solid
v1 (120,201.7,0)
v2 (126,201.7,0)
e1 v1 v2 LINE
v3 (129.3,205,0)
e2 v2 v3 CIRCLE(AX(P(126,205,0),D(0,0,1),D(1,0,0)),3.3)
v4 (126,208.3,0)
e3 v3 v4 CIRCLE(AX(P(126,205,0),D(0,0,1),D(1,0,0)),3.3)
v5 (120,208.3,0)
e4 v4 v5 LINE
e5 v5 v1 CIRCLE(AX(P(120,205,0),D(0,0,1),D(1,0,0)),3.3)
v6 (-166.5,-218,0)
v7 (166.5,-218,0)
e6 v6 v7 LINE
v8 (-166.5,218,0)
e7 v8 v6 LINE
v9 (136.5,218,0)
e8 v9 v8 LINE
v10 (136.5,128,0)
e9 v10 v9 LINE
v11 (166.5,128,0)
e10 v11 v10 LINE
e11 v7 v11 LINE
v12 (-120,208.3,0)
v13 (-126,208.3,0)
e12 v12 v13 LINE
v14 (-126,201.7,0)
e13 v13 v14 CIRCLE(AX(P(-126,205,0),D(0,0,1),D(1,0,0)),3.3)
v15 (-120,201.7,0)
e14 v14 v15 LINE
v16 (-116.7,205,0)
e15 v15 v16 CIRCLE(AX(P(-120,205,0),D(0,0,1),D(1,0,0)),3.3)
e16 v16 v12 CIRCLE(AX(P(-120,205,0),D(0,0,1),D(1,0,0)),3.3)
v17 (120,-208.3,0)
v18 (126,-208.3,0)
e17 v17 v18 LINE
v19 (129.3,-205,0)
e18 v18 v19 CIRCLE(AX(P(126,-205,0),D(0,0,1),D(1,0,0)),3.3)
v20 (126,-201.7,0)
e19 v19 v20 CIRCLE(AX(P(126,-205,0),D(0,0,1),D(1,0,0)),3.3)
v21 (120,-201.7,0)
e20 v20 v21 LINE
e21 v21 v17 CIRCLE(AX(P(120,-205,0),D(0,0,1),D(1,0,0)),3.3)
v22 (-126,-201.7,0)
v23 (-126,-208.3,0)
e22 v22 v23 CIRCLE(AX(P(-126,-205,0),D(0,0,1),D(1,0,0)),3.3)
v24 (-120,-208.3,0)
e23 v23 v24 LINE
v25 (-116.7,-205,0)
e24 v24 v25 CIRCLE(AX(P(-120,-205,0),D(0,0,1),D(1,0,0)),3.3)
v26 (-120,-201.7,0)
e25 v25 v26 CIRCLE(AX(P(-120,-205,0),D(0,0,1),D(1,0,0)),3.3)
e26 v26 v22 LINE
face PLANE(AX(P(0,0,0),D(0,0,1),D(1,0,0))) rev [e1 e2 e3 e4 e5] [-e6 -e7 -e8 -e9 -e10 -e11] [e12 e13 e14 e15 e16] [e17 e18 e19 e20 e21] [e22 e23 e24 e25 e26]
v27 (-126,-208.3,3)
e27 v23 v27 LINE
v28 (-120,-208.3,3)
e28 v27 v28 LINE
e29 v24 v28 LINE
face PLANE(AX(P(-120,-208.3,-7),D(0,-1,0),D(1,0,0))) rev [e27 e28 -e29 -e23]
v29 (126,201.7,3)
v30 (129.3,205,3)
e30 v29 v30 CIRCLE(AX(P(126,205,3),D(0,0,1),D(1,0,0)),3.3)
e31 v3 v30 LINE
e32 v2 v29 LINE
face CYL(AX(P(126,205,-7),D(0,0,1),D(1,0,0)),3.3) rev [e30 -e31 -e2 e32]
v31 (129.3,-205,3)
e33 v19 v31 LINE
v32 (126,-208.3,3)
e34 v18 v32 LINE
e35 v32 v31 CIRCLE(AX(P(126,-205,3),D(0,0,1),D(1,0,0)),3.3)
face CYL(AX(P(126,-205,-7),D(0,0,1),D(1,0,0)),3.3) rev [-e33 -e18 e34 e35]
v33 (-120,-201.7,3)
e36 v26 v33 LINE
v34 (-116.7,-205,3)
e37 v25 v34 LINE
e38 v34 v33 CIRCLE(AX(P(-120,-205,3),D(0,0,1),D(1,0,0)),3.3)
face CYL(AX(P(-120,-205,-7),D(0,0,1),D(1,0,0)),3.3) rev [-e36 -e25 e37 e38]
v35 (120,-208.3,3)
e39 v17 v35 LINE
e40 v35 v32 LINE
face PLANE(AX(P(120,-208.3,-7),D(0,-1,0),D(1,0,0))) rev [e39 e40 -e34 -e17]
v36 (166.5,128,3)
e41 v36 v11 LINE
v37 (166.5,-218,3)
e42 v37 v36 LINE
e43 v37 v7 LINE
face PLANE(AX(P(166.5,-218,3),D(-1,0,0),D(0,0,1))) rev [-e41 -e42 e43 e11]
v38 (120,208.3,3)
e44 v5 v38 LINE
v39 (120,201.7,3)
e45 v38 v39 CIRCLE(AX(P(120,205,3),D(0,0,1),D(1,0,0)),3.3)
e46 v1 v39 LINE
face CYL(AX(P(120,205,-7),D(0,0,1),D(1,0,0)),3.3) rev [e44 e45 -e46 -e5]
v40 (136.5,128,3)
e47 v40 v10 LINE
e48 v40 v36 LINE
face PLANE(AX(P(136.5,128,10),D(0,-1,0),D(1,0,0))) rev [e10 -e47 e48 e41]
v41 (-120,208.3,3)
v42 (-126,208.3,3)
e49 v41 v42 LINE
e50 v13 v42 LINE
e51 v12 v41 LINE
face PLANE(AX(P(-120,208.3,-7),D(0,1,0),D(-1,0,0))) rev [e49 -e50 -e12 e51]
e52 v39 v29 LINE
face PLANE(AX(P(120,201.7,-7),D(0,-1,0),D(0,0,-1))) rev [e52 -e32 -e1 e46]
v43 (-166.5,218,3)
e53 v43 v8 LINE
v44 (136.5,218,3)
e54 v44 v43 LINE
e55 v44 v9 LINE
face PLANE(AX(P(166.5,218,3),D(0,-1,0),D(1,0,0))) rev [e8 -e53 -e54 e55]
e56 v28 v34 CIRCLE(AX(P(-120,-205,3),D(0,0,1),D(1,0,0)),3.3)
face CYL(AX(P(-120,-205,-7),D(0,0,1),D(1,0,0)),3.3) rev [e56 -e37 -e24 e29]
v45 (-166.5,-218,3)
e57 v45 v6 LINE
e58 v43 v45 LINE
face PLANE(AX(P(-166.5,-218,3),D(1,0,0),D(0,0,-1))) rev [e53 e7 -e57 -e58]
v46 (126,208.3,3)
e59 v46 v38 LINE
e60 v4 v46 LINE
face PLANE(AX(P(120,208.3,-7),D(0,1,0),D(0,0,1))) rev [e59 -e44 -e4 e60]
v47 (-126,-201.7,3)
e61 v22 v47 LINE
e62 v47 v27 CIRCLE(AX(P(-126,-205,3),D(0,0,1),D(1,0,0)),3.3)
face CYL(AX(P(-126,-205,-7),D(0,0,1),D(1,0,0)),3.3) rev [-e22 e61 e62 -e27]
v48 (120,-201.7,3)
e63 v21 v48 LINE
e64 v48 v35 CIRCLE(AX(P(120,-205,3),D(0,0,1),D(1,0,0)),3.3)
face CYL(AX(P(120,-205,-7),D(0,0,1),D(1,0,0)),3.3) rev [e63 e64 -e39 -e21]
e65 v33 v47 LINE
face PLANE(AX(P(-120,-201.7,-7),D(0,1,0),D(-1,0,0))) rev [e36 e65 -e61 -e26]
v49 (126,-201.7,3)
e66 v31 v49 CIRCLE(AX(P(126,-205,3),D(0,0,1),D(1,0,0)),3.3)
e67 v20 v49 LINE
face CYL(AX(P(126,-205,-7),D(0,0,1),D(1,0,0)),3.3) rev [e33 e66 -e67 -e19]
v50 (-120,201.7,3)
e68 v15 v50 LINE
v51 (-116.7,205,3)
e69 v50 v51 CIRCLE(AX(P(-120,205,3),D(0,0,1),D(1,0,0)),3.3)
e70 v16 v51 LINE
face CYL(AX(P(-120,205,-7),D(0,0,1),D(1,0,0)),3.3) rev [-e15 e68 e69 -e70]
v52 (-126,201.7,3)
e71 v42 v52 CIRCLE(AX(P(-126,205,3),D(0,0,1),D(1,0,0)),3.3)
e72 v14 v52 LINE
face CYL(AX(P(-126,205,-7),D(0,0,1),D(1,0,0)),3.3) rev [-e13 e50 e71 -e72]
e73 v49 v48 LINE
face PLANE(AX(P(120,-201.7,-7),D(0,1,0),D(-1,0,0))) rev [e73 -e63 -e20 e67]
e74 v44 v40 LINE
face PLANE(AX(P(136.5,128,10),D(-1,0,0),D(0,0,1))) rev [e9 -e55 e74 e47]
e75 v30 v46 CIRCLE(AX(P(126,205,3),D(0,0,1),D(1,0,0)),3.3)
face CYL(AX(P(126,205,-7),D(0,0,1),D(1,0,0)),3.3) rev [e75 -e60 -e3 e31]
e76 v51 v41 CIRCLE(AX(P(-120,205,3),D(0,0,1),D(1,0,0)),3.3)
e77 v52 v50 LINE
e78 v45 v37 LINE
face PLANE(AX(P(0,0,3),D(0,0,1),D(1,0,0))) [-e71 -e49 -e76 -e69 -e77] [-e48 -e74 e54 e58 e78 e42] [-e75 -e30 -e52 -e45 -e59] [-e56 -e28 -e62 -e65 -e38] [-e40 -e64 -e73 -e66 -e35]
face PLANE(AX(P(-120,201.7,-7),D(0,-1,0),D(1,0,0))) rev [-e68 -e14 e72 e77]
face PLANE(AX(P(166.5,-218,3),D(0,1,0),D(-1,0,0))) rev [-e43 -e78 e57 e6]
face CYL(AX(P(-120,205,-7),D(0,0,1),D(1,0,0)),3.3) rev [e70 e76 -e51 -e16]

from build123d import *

# Parameters (mm, degrees)
SKETCH_1_W          = 333
SKETCH_1_H          = 436
EXTRUDE_1_DEPTH     = 3
SKETCH_3_W          = 30
SKETCH_3_H          = 90
CUT_EXTRUDE_2_DEPTH = 10
CUT_EXTRUDE_3_DEPTH = 10


with BuildPart() as part:
    # 草图1 → 凸台-拉伸1 (new body)
    with BuildSketch(Plane.XY):
        Rectangle(SKETCH_1_W, SKETCH_1_H)
    extrude(amount=EXTRUDE_1_DEPTH)

    # 草图3 → 切除-拉伸2 (cut)
    with BuildSketch(Plane(origin=(0, 0, 0), x_dir=(-1, 0, 0), z_dir=(0, 0, -1))):
        with Locations((-151.5, 173)):
            Rectangle(SKETCH_3_W, SKETCH_3_H)
    extrude(amount=-CUT_EXTRUDE_2_DEPTH, mode=Mode.SUBTRACT)

    # 草图4 → 切除-拉伸3 (cut)
    with BuildSketch(Plane.XY.offset(3)):
        with BuildLine():
            Line((-120, 201.7), (-126, 201.7))
            ThreePointArc((-126, 201.7), (-129.3, 205), (-126, 208.3))
            Line((-126, 208.3), (-120, 208.3))
            ThreePointArc((-120, 208.3), (-116.7, 205), (-120, 201.7))
        make_face()
        with BuildLine():
            Line((120, 208.3), (126, 208.3))
            ThreePointArc((126, 208.3), (129.3, 205), (126, 201.7))
            Line((126, 201.7), (120, 201.7))
            ThreePointArc((120, 201.7), (116.7, 205), (120, 208.3))
        make_face()
        with BuildLine():
            Line((120, -201.7), (126, -201.7))
            ThreePointArc((126, -201.7), (129.3, -205), (126, -208.3))
            Line((126, -208.3), (120, -208.3))
            ThreePointArc((120, -208.3), (116.7, -205), (120, -201.7))
        make_face()
        with BuildLine():
            Line((-120, -208.3), (-126, -208.3))
            ThreePointArc((-126, -208.3), (-129.3, -205), (-126, -201.7))
            Line((-126, -201.7), (-120, -201.7))
            ThreePointArc((-120, -201.7), (-116.7, -205), (-120, -208.3))
        make_face()
    extrude(amount=-CUT_EXTRUDE_3_DEPTH, mode=Mode.SUBTRACT)


solid = part.part
